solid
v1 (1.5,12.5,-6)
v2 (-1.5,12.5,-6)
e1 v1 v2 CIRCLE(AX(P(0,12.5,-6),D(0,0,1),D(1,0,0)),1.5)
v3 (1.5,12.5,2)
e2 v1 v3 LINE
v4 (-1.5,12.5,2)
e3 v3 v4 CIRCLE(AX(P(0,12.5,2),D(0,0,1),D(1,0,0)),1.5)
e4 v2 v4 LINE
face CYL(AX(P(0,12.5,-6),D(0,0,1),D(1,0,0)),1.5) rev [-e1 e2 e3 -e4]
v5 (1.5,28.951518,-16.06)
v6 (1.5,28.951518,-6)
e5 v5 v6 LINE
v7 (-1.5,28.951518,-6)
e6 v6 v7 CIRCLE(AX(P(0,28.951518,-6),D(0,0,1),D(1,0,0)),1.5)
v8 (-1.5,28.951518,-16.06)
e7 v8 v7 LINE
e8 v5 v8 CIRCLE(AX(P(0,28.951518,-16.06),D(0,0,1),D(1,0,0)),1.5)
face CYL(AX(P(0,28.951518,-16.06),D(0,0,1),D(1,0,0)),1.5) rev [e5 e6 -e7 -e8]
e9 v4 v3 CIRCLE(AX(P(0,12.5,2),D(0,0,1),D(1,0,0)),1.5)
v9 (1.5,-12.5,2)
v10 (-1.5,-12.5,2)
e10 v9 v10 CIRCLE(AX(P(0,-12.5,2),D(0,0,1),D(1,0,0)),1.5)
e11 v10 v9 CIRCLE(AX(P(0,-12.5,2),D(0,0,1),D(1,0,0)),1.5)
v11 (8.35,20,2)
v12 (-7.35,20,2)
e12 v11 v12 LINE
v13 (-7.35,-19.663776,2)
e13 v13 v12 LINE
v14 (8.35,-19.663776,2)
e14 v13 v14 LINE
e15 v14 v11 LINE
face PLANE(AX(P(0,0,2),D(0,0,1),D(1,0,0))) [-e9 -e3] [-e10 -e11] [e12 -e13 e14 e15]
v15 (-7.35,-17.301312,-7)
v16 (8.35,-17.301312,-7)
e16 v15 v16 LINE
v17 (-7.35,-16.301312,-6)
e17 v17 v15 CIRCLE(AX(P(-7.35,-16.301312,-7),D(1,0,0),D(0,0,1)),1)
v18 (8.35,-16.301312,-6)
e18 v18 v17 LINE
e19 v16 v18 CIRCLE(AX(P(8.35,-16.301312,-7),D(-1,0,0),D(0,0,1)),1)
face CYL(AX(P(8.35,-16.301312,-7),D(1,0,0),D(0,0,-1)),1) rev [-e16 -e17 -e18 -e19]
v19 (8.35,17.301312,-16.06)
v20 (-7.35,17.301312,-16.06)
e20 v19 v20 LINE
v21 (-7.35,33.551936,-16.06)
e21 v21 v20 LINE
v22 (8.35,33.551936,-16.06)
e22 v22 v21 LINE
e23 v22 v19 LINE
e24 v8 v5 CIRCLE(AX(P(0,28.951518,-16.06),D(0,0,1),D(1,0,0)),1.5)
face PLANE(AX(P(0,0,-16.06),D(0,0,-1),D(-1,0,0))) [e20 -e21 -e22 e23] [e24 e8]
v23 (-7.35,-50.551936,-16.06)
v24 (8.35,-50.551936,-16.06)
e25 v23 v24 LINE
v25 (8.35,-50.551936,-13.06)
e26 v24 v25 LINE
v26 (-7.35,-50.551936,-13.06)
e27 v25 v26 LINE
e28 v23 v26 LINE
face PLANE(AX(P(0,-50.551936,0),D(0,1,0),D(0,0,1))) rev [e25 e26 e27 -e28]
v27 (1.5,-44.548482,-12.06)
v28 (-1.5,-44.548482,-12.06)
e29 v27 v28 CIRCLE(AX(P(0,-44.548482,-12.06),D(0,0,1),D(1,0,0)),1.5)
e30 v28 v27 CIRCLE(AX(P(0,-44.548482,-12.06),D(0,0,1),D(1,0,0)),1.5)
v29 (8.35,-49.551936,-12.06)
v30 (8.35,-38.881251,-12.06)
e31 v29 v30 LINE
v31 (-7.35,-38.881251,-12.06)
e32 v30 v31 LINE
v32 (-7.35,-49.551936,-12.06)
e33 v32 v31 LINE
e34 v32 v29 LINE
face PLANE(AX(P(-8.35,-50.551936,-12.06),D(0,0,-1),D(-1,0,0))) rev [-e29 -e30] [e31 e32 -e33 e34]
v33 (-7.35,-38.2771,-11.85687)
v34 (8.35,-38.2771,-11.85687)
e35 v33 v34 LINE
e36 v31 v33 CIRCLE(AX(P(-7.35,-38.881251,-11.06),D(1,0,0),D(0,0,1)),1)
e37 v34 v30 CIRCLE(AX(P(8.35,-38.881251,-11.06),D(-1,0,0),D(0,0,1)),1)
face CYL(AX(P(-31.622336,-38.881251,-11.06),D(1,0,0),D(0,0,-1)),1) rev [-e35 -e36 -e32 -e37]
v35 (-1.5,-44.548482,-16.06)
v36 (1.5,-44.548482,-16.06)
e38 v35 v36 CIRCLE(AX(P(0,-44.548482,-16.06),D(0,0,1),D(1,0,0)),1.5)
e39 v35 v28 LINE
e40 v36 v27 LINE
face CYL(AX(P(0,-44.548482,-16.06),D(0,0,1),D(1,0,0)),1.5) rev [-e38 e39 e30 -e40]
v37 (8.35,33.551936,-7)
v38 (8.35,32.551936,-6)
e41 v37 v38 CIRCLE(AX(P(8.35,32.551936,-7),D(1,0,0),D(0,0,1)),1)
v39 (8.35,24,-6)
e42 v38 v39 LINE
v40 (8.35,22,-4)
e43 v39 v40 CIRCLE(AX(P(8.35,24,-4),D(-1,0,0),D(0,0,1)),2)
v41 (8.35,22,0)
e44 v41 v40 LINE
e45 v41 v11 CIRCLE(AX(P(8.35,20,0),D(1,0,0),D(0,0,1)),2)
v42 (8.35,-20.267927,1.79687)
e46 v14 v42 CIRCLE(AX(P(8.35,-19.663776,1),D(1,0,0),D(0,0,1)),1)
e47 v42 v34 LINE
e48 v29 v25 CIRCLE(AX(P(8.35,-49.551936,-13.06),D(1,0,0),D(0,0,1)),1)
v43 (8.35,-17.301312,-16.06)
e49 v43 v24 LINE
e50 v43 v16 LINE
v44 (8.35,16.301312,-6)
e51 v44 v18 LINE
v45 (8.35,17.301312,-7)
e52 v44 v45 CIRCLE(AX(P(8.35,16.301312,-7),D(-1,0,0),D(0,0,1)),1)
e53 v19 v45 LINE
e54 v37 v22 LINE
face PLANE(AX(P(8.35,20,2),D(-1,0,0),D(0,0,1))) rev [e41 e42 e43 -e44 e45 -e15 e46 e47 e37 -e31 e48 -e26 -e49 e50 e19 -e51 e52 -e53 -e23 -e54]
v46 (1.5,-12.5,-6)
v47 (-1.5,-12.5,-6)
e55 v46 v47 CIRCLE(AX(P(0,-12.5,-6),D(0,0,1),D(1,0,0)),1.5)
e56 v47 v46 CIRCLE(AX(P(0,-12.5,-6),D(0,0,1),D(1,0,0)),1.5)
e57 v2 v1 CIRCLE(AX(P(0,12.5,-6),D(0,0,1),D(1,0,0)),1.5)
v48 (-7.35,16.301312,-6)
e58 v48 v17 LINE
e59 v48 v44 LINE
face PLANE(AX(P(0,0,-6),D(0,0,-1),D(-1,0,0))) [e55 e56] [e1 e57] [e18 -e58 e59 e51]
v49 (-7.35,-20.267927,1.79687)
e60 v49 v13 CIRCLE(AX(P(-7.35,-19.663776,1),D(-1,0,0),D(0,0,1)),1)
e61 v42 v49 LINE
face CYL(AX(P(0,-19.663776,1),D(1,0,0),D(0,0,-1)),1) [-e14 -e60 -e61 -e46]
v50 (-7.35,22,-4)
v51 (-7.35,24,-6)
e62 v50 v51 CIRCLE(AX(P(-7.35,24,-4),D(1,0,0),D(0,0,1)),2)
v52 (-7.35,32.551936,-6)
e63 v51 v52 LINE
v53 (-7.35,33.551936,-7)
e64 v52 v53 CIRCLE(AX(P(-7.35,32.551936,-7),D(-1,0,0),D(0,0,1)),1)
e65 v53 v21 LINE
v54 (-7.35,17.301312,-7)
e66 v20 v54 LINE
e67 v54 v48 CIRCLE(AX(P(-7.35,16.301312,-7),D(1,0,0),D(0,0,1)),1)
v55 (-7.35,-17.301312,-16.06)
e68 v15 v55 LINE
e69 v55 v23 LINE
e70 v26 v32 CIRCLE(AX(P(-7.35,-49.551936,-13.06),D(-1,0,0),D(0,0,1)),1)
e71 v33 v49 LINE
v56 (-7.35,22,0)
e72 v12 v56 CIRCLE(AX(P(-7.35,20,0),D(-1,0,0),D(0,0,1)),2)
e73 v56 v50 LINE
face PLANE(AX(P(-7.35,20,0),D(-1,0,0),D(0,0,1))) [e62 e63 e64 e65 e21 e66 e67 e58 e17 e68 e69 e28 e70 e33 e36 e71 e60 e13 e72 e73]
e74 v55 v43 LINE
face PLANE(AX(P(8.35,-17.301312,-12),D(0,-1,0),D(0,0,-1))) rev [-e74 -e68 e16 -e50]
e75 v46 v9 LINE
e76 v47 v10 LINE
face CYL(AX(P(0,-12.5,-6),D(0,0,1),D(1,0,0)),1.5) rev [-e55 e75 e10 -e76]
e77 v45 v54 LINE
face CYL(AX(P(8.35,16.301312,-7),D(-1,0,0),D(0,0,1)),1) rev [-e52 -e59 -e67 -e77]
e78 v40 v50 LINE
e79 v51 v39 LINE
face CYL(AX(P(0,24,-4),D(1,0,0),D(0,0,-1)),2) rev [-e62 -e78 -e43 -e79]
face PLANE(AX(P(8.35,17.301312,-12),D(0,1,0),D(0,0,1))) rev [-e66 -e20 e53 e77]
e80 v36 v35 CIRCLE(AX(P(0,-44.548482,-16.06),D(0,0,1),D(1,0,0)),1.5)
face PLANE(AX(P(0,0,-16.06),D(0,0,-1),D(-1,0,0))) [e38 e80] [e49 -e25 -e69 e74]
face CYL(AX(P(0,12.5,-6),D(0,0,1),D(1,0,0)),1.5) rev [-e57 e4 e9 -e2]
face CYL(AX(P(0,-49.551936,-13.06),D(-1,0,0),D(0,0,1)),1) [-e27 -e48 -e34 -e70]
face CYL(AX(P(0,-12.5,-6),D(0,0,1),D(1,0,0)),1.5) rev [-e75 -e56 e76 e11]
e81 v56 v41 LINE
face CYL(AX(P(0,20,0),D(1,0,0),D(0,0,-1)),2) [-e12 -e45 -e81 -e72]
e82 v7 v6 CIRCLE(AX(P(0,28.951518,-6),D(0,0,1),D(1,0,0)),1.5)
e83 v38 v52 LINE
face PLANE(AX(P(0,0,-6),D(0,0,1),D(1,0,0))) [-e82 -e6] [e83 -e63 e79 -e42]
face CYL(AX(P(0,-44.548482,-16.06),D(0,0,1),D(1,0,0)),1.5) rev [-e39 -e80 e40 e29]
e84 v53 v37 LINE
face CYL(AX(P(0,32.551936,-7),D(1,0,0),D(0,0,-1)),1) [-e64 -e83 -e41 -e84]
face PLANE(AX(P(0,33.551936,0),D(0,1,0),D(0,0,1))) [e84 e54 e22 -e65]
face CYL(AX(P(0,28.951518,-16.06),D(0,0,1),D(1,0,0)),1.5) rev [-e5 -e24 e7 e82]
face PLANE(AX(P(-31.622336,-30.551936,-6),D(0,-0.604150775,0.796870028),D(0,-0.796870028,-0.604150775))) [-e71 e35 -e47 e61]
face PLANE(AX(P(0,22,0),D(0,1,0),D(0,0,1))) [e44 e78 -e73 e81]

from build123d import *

# Parameters (mm, degrees)
SKETCH1_W            = 16.7
SKETCH1_H            = 40
BOSS_EXTRUDE1_DEPTH  = 2
SKETCH12_W           = 16.7
SKETCH12_H           = 40
BOSS_EXTRUDE4_DEPTH  = 6
SKETCH15_R           = 1.5
CUT_EXTRUDE3_DEPTH   = 24.102434937
SKETCH16_W           = 16.7
SKETCH16_H           = 13.250623967
BOSS_EXTRUDE5_DEPTH  = 6
SKETCH21_W           = 16.7
SKETCH21_H           = 13.250623967
BOSS_EXTRUDE10_DEPTH = 4.06
SKETCH22_W           = 16.7
SKETCH22_H           = 4
BOSS_EXTRUDE11_DEPTH = 20
BOSS_EXTRUDE12_DEPTH = 16.7
SKETCH24_R           = 1.5
CUT_EXTRUDE5_DEPTH   = 54.131010889
SKETCH25_W           = 16.7
SKETCH25_H           = 8
BOSS_EXTRUDE13_DEPTH = 2
FILLET1_R            = 2
FILLET2_R            = 2
SKETCH27_W           = 16.7
SKETCH27_H           = 10.06
BOSS_EXTRUDE14_DEPTH = 3
SKETCH26_R           = 1.5
CUT_EXTRUDE6_DEPTH   = 53.215173256
CUT_EXTRUDE7_DEPTH   = 1
FILLET3_R            = 1


with BuildPart() as part:
    # Sketch1 → Boss-Extrude1 (new body)
    with BuildSketch(Plane.XY):
        Rectangle(SKETCH1_W, SKETCH1_H)
    extrude(amount=BOSS_EXTRUDE1_DEPTH)

    # Sketch12 → Boss-Extrude4 (add)
    with BuildSketch(Plane(origin=(0, 0, 0), x_dir=(-1, 0, 0), z_dir=(0, 0, -1))):
        Rectangle(SKETCH12_W, SKETCH12_H)
    extrude(amount=BOSS_EXTRUDE4_DEPTH)

    # Sketch15 → Cut-Extrude3 (cut, through all)
    with BuildSketch(Plane.XY.offset(2)):
        with Locations((0, 12.5)):
            Circle(SKETCH15_R)
        with Locations((0, -12.5)):
            Circle(SKETCH15_R)
    extrude(amount=-CUT_EXTRUDE3_DEPTH, mode=Mode.SUBTRACT)

    # Sketch16 → Boss-Extrude5 (add)
    with BuildSketch(Plane(origin=(0, 0, -6), x_dir=(-1, 0, 0), z_dir=(0, 0, -1))):
        with Locations((0, 23.926623866)):
            Rectangle(SKETCH16_W, SKETCH16_H)
        with Locations((0, -23.926623866)):
            Rectangle(SKETCH16_W, SKETCH16_H)
    extrude(amount=BOSS_EXTRUDE5_DEPTH)

    # Sketch21 → Boss-Extrude10 (add)
    with BuildSketch(Plane(origin=(0, 0, -12), x_dir=(-1, 0, 0), z_dir=(0, 0, -1))):
        with Locations((0, -23.926623866)):
            Rectangle(SKETCH21_W, SKETCH21_H)
        with Locations((0, 23.926623866)):
            Rectangle(SKETCH21_W, SKETCH21_H)
    extrude(amount=BOSS_EXTRUDE10_DEPTH)

    # Sketch22 → Boss-Extrude11 (add)
    with BuildSketch(Plane.XZ.offset(30.551935849)):
        with Locations((0, -14.06)):
            Rectangle(SKETCH22_W, SKETCH22_H)
    extrude(amount=BOSS_EXTRUDE11_DEPTH)

    # Sketch23 → Boss-Extrude12 (add)
    with BuildSketch(Plane(origin=(8.35, 0, 0), x_dir=(0, 0, -1), z_dir=(1, 0, 0))):
        Polygon((-2, -20), (6, -30.551935849), (12.06, -38.545027255), (12.06, -20), align=None)
    extrude(amount=-BOSS_EXTRUDE12_DEPTH)

    # Sketch24 → Cut-Extrude5 (cut, through all)
    with BuildSketch(Plane.XY.offset(-12.06)):
        with Locations((0, -44.548481552)):
            Circle(SKETCH24_R)
        with Locations((0, 44.548481552)):
            Circle(SKETCH24_R)
    extrude(amount=-CUT_EXTRUDE5_DEPTH, mode=Mode.SUBTRACT)

    # Sketch25 → Boss-Extrude13 (add)
    with BuildSketch(Plane(origin=(0, 20, 0), x_dir=(1, 0, 0), z_dir=(0, 1, 0))):
        with Locations((0, 2)):
            Rectangle(SKETCH25_W, SKETCH25_H)
    extrude(amount=BOSS_EXTRUDE13_DEPTH)

    # Fillet1
    fillet1_edges = [part.edges().sort_by_distance(p)[0] for p in [
        (0, 22, 2),
    ]]
    fillet(fillet1_edges, radius=FILLET1_R)

    # Fillet2
    fillet2_edges = [part.edges().sort_by_distance(p)[0] for p in [
        (0, 22, -6),
    ]]
    fillet(fillet2_edges, radius=FILLET2_R)

    # Sketch27 → Boss-Extrude14 (add)
    with BuildSketch(Plane(origin=(0, 30.551935849, 0), x_dir=(1, 0, 0), z_dir=(0, 1, 0))):
        with Locations((0, 11.03)):
            Rectangle(SKETCH27_W, SKETCH27_H)
    extrude(amount=BOSS_EXTRUDE14_DEPTH)

    # Sketch26 → Cut-Extrude6 (cut, through all)
    with BuildSketch(Plane.XY.offset(-6)):
        with Locations((0, 28.951518448)):
            Circle(SKETCH26_R)
    extrude(amount=-CUT_EXTRUDE6_DEPTH, mode=Mode.SUBTRACT)

    # Sketch28 → Cut-Extrude7 (cut)
    with BuildSketch(Plane.ZY.offset(8.35)):
        with BuildLine():
            Line((2, -20), (2, 20))
            ThreePointArc((2, 20), (1.414213562, 21.414213562), (0, 22))
            Line((0, 22), (-4, 22))
            ThreePointArc((-4, 22), (-5.414213562, 22.585786438), (-6, 24))
            Line((-6, 24), (-6, 33.551935849))
            Line((-6, 33.551935849), (-16.06, 33.551935849))
            Line((-16.06, 33.551935849), (-16.06, 17.301311882))
            Line((-16.06, 17.301311882), (-6, 17.301311882))
            Line((-6, 17.301311882), (-6, -17.301311882))
            Line((-6, -17.301311882), (-16.06, -17.301311882))
            Line((-16.06, -17.301311882), (-16.06, -50.551935849))
            Line((-16.06, -50.551935849), (-12.06, -50.551935849))
            Line((-12.06, -50.551935849), (-12.06, -38.545027255))
            Line((-12.06, -38.545027255), (2, -20))
        make_face()
    extrude(amount=-CUT_EXTRUDE7_DEPTH, mode=Mode.SUBTRACT)

    # Fillet3
    fillet3_edges = [part.edges().sort_by_distance(p)[0] for p in [
        (0.5, 33.551935849, -6),
        (0.5, -20, 2),
        (0.5, -38.545027255, -12.06),
        (0.5, -17.301311882, -6),
        (0.5, 17.301311882, -6),
        (0.5, -50.551935849, -12.06),
    ]]
    fillet(fillet3_edges, radius=FILLET3_R)


solid = part.part
